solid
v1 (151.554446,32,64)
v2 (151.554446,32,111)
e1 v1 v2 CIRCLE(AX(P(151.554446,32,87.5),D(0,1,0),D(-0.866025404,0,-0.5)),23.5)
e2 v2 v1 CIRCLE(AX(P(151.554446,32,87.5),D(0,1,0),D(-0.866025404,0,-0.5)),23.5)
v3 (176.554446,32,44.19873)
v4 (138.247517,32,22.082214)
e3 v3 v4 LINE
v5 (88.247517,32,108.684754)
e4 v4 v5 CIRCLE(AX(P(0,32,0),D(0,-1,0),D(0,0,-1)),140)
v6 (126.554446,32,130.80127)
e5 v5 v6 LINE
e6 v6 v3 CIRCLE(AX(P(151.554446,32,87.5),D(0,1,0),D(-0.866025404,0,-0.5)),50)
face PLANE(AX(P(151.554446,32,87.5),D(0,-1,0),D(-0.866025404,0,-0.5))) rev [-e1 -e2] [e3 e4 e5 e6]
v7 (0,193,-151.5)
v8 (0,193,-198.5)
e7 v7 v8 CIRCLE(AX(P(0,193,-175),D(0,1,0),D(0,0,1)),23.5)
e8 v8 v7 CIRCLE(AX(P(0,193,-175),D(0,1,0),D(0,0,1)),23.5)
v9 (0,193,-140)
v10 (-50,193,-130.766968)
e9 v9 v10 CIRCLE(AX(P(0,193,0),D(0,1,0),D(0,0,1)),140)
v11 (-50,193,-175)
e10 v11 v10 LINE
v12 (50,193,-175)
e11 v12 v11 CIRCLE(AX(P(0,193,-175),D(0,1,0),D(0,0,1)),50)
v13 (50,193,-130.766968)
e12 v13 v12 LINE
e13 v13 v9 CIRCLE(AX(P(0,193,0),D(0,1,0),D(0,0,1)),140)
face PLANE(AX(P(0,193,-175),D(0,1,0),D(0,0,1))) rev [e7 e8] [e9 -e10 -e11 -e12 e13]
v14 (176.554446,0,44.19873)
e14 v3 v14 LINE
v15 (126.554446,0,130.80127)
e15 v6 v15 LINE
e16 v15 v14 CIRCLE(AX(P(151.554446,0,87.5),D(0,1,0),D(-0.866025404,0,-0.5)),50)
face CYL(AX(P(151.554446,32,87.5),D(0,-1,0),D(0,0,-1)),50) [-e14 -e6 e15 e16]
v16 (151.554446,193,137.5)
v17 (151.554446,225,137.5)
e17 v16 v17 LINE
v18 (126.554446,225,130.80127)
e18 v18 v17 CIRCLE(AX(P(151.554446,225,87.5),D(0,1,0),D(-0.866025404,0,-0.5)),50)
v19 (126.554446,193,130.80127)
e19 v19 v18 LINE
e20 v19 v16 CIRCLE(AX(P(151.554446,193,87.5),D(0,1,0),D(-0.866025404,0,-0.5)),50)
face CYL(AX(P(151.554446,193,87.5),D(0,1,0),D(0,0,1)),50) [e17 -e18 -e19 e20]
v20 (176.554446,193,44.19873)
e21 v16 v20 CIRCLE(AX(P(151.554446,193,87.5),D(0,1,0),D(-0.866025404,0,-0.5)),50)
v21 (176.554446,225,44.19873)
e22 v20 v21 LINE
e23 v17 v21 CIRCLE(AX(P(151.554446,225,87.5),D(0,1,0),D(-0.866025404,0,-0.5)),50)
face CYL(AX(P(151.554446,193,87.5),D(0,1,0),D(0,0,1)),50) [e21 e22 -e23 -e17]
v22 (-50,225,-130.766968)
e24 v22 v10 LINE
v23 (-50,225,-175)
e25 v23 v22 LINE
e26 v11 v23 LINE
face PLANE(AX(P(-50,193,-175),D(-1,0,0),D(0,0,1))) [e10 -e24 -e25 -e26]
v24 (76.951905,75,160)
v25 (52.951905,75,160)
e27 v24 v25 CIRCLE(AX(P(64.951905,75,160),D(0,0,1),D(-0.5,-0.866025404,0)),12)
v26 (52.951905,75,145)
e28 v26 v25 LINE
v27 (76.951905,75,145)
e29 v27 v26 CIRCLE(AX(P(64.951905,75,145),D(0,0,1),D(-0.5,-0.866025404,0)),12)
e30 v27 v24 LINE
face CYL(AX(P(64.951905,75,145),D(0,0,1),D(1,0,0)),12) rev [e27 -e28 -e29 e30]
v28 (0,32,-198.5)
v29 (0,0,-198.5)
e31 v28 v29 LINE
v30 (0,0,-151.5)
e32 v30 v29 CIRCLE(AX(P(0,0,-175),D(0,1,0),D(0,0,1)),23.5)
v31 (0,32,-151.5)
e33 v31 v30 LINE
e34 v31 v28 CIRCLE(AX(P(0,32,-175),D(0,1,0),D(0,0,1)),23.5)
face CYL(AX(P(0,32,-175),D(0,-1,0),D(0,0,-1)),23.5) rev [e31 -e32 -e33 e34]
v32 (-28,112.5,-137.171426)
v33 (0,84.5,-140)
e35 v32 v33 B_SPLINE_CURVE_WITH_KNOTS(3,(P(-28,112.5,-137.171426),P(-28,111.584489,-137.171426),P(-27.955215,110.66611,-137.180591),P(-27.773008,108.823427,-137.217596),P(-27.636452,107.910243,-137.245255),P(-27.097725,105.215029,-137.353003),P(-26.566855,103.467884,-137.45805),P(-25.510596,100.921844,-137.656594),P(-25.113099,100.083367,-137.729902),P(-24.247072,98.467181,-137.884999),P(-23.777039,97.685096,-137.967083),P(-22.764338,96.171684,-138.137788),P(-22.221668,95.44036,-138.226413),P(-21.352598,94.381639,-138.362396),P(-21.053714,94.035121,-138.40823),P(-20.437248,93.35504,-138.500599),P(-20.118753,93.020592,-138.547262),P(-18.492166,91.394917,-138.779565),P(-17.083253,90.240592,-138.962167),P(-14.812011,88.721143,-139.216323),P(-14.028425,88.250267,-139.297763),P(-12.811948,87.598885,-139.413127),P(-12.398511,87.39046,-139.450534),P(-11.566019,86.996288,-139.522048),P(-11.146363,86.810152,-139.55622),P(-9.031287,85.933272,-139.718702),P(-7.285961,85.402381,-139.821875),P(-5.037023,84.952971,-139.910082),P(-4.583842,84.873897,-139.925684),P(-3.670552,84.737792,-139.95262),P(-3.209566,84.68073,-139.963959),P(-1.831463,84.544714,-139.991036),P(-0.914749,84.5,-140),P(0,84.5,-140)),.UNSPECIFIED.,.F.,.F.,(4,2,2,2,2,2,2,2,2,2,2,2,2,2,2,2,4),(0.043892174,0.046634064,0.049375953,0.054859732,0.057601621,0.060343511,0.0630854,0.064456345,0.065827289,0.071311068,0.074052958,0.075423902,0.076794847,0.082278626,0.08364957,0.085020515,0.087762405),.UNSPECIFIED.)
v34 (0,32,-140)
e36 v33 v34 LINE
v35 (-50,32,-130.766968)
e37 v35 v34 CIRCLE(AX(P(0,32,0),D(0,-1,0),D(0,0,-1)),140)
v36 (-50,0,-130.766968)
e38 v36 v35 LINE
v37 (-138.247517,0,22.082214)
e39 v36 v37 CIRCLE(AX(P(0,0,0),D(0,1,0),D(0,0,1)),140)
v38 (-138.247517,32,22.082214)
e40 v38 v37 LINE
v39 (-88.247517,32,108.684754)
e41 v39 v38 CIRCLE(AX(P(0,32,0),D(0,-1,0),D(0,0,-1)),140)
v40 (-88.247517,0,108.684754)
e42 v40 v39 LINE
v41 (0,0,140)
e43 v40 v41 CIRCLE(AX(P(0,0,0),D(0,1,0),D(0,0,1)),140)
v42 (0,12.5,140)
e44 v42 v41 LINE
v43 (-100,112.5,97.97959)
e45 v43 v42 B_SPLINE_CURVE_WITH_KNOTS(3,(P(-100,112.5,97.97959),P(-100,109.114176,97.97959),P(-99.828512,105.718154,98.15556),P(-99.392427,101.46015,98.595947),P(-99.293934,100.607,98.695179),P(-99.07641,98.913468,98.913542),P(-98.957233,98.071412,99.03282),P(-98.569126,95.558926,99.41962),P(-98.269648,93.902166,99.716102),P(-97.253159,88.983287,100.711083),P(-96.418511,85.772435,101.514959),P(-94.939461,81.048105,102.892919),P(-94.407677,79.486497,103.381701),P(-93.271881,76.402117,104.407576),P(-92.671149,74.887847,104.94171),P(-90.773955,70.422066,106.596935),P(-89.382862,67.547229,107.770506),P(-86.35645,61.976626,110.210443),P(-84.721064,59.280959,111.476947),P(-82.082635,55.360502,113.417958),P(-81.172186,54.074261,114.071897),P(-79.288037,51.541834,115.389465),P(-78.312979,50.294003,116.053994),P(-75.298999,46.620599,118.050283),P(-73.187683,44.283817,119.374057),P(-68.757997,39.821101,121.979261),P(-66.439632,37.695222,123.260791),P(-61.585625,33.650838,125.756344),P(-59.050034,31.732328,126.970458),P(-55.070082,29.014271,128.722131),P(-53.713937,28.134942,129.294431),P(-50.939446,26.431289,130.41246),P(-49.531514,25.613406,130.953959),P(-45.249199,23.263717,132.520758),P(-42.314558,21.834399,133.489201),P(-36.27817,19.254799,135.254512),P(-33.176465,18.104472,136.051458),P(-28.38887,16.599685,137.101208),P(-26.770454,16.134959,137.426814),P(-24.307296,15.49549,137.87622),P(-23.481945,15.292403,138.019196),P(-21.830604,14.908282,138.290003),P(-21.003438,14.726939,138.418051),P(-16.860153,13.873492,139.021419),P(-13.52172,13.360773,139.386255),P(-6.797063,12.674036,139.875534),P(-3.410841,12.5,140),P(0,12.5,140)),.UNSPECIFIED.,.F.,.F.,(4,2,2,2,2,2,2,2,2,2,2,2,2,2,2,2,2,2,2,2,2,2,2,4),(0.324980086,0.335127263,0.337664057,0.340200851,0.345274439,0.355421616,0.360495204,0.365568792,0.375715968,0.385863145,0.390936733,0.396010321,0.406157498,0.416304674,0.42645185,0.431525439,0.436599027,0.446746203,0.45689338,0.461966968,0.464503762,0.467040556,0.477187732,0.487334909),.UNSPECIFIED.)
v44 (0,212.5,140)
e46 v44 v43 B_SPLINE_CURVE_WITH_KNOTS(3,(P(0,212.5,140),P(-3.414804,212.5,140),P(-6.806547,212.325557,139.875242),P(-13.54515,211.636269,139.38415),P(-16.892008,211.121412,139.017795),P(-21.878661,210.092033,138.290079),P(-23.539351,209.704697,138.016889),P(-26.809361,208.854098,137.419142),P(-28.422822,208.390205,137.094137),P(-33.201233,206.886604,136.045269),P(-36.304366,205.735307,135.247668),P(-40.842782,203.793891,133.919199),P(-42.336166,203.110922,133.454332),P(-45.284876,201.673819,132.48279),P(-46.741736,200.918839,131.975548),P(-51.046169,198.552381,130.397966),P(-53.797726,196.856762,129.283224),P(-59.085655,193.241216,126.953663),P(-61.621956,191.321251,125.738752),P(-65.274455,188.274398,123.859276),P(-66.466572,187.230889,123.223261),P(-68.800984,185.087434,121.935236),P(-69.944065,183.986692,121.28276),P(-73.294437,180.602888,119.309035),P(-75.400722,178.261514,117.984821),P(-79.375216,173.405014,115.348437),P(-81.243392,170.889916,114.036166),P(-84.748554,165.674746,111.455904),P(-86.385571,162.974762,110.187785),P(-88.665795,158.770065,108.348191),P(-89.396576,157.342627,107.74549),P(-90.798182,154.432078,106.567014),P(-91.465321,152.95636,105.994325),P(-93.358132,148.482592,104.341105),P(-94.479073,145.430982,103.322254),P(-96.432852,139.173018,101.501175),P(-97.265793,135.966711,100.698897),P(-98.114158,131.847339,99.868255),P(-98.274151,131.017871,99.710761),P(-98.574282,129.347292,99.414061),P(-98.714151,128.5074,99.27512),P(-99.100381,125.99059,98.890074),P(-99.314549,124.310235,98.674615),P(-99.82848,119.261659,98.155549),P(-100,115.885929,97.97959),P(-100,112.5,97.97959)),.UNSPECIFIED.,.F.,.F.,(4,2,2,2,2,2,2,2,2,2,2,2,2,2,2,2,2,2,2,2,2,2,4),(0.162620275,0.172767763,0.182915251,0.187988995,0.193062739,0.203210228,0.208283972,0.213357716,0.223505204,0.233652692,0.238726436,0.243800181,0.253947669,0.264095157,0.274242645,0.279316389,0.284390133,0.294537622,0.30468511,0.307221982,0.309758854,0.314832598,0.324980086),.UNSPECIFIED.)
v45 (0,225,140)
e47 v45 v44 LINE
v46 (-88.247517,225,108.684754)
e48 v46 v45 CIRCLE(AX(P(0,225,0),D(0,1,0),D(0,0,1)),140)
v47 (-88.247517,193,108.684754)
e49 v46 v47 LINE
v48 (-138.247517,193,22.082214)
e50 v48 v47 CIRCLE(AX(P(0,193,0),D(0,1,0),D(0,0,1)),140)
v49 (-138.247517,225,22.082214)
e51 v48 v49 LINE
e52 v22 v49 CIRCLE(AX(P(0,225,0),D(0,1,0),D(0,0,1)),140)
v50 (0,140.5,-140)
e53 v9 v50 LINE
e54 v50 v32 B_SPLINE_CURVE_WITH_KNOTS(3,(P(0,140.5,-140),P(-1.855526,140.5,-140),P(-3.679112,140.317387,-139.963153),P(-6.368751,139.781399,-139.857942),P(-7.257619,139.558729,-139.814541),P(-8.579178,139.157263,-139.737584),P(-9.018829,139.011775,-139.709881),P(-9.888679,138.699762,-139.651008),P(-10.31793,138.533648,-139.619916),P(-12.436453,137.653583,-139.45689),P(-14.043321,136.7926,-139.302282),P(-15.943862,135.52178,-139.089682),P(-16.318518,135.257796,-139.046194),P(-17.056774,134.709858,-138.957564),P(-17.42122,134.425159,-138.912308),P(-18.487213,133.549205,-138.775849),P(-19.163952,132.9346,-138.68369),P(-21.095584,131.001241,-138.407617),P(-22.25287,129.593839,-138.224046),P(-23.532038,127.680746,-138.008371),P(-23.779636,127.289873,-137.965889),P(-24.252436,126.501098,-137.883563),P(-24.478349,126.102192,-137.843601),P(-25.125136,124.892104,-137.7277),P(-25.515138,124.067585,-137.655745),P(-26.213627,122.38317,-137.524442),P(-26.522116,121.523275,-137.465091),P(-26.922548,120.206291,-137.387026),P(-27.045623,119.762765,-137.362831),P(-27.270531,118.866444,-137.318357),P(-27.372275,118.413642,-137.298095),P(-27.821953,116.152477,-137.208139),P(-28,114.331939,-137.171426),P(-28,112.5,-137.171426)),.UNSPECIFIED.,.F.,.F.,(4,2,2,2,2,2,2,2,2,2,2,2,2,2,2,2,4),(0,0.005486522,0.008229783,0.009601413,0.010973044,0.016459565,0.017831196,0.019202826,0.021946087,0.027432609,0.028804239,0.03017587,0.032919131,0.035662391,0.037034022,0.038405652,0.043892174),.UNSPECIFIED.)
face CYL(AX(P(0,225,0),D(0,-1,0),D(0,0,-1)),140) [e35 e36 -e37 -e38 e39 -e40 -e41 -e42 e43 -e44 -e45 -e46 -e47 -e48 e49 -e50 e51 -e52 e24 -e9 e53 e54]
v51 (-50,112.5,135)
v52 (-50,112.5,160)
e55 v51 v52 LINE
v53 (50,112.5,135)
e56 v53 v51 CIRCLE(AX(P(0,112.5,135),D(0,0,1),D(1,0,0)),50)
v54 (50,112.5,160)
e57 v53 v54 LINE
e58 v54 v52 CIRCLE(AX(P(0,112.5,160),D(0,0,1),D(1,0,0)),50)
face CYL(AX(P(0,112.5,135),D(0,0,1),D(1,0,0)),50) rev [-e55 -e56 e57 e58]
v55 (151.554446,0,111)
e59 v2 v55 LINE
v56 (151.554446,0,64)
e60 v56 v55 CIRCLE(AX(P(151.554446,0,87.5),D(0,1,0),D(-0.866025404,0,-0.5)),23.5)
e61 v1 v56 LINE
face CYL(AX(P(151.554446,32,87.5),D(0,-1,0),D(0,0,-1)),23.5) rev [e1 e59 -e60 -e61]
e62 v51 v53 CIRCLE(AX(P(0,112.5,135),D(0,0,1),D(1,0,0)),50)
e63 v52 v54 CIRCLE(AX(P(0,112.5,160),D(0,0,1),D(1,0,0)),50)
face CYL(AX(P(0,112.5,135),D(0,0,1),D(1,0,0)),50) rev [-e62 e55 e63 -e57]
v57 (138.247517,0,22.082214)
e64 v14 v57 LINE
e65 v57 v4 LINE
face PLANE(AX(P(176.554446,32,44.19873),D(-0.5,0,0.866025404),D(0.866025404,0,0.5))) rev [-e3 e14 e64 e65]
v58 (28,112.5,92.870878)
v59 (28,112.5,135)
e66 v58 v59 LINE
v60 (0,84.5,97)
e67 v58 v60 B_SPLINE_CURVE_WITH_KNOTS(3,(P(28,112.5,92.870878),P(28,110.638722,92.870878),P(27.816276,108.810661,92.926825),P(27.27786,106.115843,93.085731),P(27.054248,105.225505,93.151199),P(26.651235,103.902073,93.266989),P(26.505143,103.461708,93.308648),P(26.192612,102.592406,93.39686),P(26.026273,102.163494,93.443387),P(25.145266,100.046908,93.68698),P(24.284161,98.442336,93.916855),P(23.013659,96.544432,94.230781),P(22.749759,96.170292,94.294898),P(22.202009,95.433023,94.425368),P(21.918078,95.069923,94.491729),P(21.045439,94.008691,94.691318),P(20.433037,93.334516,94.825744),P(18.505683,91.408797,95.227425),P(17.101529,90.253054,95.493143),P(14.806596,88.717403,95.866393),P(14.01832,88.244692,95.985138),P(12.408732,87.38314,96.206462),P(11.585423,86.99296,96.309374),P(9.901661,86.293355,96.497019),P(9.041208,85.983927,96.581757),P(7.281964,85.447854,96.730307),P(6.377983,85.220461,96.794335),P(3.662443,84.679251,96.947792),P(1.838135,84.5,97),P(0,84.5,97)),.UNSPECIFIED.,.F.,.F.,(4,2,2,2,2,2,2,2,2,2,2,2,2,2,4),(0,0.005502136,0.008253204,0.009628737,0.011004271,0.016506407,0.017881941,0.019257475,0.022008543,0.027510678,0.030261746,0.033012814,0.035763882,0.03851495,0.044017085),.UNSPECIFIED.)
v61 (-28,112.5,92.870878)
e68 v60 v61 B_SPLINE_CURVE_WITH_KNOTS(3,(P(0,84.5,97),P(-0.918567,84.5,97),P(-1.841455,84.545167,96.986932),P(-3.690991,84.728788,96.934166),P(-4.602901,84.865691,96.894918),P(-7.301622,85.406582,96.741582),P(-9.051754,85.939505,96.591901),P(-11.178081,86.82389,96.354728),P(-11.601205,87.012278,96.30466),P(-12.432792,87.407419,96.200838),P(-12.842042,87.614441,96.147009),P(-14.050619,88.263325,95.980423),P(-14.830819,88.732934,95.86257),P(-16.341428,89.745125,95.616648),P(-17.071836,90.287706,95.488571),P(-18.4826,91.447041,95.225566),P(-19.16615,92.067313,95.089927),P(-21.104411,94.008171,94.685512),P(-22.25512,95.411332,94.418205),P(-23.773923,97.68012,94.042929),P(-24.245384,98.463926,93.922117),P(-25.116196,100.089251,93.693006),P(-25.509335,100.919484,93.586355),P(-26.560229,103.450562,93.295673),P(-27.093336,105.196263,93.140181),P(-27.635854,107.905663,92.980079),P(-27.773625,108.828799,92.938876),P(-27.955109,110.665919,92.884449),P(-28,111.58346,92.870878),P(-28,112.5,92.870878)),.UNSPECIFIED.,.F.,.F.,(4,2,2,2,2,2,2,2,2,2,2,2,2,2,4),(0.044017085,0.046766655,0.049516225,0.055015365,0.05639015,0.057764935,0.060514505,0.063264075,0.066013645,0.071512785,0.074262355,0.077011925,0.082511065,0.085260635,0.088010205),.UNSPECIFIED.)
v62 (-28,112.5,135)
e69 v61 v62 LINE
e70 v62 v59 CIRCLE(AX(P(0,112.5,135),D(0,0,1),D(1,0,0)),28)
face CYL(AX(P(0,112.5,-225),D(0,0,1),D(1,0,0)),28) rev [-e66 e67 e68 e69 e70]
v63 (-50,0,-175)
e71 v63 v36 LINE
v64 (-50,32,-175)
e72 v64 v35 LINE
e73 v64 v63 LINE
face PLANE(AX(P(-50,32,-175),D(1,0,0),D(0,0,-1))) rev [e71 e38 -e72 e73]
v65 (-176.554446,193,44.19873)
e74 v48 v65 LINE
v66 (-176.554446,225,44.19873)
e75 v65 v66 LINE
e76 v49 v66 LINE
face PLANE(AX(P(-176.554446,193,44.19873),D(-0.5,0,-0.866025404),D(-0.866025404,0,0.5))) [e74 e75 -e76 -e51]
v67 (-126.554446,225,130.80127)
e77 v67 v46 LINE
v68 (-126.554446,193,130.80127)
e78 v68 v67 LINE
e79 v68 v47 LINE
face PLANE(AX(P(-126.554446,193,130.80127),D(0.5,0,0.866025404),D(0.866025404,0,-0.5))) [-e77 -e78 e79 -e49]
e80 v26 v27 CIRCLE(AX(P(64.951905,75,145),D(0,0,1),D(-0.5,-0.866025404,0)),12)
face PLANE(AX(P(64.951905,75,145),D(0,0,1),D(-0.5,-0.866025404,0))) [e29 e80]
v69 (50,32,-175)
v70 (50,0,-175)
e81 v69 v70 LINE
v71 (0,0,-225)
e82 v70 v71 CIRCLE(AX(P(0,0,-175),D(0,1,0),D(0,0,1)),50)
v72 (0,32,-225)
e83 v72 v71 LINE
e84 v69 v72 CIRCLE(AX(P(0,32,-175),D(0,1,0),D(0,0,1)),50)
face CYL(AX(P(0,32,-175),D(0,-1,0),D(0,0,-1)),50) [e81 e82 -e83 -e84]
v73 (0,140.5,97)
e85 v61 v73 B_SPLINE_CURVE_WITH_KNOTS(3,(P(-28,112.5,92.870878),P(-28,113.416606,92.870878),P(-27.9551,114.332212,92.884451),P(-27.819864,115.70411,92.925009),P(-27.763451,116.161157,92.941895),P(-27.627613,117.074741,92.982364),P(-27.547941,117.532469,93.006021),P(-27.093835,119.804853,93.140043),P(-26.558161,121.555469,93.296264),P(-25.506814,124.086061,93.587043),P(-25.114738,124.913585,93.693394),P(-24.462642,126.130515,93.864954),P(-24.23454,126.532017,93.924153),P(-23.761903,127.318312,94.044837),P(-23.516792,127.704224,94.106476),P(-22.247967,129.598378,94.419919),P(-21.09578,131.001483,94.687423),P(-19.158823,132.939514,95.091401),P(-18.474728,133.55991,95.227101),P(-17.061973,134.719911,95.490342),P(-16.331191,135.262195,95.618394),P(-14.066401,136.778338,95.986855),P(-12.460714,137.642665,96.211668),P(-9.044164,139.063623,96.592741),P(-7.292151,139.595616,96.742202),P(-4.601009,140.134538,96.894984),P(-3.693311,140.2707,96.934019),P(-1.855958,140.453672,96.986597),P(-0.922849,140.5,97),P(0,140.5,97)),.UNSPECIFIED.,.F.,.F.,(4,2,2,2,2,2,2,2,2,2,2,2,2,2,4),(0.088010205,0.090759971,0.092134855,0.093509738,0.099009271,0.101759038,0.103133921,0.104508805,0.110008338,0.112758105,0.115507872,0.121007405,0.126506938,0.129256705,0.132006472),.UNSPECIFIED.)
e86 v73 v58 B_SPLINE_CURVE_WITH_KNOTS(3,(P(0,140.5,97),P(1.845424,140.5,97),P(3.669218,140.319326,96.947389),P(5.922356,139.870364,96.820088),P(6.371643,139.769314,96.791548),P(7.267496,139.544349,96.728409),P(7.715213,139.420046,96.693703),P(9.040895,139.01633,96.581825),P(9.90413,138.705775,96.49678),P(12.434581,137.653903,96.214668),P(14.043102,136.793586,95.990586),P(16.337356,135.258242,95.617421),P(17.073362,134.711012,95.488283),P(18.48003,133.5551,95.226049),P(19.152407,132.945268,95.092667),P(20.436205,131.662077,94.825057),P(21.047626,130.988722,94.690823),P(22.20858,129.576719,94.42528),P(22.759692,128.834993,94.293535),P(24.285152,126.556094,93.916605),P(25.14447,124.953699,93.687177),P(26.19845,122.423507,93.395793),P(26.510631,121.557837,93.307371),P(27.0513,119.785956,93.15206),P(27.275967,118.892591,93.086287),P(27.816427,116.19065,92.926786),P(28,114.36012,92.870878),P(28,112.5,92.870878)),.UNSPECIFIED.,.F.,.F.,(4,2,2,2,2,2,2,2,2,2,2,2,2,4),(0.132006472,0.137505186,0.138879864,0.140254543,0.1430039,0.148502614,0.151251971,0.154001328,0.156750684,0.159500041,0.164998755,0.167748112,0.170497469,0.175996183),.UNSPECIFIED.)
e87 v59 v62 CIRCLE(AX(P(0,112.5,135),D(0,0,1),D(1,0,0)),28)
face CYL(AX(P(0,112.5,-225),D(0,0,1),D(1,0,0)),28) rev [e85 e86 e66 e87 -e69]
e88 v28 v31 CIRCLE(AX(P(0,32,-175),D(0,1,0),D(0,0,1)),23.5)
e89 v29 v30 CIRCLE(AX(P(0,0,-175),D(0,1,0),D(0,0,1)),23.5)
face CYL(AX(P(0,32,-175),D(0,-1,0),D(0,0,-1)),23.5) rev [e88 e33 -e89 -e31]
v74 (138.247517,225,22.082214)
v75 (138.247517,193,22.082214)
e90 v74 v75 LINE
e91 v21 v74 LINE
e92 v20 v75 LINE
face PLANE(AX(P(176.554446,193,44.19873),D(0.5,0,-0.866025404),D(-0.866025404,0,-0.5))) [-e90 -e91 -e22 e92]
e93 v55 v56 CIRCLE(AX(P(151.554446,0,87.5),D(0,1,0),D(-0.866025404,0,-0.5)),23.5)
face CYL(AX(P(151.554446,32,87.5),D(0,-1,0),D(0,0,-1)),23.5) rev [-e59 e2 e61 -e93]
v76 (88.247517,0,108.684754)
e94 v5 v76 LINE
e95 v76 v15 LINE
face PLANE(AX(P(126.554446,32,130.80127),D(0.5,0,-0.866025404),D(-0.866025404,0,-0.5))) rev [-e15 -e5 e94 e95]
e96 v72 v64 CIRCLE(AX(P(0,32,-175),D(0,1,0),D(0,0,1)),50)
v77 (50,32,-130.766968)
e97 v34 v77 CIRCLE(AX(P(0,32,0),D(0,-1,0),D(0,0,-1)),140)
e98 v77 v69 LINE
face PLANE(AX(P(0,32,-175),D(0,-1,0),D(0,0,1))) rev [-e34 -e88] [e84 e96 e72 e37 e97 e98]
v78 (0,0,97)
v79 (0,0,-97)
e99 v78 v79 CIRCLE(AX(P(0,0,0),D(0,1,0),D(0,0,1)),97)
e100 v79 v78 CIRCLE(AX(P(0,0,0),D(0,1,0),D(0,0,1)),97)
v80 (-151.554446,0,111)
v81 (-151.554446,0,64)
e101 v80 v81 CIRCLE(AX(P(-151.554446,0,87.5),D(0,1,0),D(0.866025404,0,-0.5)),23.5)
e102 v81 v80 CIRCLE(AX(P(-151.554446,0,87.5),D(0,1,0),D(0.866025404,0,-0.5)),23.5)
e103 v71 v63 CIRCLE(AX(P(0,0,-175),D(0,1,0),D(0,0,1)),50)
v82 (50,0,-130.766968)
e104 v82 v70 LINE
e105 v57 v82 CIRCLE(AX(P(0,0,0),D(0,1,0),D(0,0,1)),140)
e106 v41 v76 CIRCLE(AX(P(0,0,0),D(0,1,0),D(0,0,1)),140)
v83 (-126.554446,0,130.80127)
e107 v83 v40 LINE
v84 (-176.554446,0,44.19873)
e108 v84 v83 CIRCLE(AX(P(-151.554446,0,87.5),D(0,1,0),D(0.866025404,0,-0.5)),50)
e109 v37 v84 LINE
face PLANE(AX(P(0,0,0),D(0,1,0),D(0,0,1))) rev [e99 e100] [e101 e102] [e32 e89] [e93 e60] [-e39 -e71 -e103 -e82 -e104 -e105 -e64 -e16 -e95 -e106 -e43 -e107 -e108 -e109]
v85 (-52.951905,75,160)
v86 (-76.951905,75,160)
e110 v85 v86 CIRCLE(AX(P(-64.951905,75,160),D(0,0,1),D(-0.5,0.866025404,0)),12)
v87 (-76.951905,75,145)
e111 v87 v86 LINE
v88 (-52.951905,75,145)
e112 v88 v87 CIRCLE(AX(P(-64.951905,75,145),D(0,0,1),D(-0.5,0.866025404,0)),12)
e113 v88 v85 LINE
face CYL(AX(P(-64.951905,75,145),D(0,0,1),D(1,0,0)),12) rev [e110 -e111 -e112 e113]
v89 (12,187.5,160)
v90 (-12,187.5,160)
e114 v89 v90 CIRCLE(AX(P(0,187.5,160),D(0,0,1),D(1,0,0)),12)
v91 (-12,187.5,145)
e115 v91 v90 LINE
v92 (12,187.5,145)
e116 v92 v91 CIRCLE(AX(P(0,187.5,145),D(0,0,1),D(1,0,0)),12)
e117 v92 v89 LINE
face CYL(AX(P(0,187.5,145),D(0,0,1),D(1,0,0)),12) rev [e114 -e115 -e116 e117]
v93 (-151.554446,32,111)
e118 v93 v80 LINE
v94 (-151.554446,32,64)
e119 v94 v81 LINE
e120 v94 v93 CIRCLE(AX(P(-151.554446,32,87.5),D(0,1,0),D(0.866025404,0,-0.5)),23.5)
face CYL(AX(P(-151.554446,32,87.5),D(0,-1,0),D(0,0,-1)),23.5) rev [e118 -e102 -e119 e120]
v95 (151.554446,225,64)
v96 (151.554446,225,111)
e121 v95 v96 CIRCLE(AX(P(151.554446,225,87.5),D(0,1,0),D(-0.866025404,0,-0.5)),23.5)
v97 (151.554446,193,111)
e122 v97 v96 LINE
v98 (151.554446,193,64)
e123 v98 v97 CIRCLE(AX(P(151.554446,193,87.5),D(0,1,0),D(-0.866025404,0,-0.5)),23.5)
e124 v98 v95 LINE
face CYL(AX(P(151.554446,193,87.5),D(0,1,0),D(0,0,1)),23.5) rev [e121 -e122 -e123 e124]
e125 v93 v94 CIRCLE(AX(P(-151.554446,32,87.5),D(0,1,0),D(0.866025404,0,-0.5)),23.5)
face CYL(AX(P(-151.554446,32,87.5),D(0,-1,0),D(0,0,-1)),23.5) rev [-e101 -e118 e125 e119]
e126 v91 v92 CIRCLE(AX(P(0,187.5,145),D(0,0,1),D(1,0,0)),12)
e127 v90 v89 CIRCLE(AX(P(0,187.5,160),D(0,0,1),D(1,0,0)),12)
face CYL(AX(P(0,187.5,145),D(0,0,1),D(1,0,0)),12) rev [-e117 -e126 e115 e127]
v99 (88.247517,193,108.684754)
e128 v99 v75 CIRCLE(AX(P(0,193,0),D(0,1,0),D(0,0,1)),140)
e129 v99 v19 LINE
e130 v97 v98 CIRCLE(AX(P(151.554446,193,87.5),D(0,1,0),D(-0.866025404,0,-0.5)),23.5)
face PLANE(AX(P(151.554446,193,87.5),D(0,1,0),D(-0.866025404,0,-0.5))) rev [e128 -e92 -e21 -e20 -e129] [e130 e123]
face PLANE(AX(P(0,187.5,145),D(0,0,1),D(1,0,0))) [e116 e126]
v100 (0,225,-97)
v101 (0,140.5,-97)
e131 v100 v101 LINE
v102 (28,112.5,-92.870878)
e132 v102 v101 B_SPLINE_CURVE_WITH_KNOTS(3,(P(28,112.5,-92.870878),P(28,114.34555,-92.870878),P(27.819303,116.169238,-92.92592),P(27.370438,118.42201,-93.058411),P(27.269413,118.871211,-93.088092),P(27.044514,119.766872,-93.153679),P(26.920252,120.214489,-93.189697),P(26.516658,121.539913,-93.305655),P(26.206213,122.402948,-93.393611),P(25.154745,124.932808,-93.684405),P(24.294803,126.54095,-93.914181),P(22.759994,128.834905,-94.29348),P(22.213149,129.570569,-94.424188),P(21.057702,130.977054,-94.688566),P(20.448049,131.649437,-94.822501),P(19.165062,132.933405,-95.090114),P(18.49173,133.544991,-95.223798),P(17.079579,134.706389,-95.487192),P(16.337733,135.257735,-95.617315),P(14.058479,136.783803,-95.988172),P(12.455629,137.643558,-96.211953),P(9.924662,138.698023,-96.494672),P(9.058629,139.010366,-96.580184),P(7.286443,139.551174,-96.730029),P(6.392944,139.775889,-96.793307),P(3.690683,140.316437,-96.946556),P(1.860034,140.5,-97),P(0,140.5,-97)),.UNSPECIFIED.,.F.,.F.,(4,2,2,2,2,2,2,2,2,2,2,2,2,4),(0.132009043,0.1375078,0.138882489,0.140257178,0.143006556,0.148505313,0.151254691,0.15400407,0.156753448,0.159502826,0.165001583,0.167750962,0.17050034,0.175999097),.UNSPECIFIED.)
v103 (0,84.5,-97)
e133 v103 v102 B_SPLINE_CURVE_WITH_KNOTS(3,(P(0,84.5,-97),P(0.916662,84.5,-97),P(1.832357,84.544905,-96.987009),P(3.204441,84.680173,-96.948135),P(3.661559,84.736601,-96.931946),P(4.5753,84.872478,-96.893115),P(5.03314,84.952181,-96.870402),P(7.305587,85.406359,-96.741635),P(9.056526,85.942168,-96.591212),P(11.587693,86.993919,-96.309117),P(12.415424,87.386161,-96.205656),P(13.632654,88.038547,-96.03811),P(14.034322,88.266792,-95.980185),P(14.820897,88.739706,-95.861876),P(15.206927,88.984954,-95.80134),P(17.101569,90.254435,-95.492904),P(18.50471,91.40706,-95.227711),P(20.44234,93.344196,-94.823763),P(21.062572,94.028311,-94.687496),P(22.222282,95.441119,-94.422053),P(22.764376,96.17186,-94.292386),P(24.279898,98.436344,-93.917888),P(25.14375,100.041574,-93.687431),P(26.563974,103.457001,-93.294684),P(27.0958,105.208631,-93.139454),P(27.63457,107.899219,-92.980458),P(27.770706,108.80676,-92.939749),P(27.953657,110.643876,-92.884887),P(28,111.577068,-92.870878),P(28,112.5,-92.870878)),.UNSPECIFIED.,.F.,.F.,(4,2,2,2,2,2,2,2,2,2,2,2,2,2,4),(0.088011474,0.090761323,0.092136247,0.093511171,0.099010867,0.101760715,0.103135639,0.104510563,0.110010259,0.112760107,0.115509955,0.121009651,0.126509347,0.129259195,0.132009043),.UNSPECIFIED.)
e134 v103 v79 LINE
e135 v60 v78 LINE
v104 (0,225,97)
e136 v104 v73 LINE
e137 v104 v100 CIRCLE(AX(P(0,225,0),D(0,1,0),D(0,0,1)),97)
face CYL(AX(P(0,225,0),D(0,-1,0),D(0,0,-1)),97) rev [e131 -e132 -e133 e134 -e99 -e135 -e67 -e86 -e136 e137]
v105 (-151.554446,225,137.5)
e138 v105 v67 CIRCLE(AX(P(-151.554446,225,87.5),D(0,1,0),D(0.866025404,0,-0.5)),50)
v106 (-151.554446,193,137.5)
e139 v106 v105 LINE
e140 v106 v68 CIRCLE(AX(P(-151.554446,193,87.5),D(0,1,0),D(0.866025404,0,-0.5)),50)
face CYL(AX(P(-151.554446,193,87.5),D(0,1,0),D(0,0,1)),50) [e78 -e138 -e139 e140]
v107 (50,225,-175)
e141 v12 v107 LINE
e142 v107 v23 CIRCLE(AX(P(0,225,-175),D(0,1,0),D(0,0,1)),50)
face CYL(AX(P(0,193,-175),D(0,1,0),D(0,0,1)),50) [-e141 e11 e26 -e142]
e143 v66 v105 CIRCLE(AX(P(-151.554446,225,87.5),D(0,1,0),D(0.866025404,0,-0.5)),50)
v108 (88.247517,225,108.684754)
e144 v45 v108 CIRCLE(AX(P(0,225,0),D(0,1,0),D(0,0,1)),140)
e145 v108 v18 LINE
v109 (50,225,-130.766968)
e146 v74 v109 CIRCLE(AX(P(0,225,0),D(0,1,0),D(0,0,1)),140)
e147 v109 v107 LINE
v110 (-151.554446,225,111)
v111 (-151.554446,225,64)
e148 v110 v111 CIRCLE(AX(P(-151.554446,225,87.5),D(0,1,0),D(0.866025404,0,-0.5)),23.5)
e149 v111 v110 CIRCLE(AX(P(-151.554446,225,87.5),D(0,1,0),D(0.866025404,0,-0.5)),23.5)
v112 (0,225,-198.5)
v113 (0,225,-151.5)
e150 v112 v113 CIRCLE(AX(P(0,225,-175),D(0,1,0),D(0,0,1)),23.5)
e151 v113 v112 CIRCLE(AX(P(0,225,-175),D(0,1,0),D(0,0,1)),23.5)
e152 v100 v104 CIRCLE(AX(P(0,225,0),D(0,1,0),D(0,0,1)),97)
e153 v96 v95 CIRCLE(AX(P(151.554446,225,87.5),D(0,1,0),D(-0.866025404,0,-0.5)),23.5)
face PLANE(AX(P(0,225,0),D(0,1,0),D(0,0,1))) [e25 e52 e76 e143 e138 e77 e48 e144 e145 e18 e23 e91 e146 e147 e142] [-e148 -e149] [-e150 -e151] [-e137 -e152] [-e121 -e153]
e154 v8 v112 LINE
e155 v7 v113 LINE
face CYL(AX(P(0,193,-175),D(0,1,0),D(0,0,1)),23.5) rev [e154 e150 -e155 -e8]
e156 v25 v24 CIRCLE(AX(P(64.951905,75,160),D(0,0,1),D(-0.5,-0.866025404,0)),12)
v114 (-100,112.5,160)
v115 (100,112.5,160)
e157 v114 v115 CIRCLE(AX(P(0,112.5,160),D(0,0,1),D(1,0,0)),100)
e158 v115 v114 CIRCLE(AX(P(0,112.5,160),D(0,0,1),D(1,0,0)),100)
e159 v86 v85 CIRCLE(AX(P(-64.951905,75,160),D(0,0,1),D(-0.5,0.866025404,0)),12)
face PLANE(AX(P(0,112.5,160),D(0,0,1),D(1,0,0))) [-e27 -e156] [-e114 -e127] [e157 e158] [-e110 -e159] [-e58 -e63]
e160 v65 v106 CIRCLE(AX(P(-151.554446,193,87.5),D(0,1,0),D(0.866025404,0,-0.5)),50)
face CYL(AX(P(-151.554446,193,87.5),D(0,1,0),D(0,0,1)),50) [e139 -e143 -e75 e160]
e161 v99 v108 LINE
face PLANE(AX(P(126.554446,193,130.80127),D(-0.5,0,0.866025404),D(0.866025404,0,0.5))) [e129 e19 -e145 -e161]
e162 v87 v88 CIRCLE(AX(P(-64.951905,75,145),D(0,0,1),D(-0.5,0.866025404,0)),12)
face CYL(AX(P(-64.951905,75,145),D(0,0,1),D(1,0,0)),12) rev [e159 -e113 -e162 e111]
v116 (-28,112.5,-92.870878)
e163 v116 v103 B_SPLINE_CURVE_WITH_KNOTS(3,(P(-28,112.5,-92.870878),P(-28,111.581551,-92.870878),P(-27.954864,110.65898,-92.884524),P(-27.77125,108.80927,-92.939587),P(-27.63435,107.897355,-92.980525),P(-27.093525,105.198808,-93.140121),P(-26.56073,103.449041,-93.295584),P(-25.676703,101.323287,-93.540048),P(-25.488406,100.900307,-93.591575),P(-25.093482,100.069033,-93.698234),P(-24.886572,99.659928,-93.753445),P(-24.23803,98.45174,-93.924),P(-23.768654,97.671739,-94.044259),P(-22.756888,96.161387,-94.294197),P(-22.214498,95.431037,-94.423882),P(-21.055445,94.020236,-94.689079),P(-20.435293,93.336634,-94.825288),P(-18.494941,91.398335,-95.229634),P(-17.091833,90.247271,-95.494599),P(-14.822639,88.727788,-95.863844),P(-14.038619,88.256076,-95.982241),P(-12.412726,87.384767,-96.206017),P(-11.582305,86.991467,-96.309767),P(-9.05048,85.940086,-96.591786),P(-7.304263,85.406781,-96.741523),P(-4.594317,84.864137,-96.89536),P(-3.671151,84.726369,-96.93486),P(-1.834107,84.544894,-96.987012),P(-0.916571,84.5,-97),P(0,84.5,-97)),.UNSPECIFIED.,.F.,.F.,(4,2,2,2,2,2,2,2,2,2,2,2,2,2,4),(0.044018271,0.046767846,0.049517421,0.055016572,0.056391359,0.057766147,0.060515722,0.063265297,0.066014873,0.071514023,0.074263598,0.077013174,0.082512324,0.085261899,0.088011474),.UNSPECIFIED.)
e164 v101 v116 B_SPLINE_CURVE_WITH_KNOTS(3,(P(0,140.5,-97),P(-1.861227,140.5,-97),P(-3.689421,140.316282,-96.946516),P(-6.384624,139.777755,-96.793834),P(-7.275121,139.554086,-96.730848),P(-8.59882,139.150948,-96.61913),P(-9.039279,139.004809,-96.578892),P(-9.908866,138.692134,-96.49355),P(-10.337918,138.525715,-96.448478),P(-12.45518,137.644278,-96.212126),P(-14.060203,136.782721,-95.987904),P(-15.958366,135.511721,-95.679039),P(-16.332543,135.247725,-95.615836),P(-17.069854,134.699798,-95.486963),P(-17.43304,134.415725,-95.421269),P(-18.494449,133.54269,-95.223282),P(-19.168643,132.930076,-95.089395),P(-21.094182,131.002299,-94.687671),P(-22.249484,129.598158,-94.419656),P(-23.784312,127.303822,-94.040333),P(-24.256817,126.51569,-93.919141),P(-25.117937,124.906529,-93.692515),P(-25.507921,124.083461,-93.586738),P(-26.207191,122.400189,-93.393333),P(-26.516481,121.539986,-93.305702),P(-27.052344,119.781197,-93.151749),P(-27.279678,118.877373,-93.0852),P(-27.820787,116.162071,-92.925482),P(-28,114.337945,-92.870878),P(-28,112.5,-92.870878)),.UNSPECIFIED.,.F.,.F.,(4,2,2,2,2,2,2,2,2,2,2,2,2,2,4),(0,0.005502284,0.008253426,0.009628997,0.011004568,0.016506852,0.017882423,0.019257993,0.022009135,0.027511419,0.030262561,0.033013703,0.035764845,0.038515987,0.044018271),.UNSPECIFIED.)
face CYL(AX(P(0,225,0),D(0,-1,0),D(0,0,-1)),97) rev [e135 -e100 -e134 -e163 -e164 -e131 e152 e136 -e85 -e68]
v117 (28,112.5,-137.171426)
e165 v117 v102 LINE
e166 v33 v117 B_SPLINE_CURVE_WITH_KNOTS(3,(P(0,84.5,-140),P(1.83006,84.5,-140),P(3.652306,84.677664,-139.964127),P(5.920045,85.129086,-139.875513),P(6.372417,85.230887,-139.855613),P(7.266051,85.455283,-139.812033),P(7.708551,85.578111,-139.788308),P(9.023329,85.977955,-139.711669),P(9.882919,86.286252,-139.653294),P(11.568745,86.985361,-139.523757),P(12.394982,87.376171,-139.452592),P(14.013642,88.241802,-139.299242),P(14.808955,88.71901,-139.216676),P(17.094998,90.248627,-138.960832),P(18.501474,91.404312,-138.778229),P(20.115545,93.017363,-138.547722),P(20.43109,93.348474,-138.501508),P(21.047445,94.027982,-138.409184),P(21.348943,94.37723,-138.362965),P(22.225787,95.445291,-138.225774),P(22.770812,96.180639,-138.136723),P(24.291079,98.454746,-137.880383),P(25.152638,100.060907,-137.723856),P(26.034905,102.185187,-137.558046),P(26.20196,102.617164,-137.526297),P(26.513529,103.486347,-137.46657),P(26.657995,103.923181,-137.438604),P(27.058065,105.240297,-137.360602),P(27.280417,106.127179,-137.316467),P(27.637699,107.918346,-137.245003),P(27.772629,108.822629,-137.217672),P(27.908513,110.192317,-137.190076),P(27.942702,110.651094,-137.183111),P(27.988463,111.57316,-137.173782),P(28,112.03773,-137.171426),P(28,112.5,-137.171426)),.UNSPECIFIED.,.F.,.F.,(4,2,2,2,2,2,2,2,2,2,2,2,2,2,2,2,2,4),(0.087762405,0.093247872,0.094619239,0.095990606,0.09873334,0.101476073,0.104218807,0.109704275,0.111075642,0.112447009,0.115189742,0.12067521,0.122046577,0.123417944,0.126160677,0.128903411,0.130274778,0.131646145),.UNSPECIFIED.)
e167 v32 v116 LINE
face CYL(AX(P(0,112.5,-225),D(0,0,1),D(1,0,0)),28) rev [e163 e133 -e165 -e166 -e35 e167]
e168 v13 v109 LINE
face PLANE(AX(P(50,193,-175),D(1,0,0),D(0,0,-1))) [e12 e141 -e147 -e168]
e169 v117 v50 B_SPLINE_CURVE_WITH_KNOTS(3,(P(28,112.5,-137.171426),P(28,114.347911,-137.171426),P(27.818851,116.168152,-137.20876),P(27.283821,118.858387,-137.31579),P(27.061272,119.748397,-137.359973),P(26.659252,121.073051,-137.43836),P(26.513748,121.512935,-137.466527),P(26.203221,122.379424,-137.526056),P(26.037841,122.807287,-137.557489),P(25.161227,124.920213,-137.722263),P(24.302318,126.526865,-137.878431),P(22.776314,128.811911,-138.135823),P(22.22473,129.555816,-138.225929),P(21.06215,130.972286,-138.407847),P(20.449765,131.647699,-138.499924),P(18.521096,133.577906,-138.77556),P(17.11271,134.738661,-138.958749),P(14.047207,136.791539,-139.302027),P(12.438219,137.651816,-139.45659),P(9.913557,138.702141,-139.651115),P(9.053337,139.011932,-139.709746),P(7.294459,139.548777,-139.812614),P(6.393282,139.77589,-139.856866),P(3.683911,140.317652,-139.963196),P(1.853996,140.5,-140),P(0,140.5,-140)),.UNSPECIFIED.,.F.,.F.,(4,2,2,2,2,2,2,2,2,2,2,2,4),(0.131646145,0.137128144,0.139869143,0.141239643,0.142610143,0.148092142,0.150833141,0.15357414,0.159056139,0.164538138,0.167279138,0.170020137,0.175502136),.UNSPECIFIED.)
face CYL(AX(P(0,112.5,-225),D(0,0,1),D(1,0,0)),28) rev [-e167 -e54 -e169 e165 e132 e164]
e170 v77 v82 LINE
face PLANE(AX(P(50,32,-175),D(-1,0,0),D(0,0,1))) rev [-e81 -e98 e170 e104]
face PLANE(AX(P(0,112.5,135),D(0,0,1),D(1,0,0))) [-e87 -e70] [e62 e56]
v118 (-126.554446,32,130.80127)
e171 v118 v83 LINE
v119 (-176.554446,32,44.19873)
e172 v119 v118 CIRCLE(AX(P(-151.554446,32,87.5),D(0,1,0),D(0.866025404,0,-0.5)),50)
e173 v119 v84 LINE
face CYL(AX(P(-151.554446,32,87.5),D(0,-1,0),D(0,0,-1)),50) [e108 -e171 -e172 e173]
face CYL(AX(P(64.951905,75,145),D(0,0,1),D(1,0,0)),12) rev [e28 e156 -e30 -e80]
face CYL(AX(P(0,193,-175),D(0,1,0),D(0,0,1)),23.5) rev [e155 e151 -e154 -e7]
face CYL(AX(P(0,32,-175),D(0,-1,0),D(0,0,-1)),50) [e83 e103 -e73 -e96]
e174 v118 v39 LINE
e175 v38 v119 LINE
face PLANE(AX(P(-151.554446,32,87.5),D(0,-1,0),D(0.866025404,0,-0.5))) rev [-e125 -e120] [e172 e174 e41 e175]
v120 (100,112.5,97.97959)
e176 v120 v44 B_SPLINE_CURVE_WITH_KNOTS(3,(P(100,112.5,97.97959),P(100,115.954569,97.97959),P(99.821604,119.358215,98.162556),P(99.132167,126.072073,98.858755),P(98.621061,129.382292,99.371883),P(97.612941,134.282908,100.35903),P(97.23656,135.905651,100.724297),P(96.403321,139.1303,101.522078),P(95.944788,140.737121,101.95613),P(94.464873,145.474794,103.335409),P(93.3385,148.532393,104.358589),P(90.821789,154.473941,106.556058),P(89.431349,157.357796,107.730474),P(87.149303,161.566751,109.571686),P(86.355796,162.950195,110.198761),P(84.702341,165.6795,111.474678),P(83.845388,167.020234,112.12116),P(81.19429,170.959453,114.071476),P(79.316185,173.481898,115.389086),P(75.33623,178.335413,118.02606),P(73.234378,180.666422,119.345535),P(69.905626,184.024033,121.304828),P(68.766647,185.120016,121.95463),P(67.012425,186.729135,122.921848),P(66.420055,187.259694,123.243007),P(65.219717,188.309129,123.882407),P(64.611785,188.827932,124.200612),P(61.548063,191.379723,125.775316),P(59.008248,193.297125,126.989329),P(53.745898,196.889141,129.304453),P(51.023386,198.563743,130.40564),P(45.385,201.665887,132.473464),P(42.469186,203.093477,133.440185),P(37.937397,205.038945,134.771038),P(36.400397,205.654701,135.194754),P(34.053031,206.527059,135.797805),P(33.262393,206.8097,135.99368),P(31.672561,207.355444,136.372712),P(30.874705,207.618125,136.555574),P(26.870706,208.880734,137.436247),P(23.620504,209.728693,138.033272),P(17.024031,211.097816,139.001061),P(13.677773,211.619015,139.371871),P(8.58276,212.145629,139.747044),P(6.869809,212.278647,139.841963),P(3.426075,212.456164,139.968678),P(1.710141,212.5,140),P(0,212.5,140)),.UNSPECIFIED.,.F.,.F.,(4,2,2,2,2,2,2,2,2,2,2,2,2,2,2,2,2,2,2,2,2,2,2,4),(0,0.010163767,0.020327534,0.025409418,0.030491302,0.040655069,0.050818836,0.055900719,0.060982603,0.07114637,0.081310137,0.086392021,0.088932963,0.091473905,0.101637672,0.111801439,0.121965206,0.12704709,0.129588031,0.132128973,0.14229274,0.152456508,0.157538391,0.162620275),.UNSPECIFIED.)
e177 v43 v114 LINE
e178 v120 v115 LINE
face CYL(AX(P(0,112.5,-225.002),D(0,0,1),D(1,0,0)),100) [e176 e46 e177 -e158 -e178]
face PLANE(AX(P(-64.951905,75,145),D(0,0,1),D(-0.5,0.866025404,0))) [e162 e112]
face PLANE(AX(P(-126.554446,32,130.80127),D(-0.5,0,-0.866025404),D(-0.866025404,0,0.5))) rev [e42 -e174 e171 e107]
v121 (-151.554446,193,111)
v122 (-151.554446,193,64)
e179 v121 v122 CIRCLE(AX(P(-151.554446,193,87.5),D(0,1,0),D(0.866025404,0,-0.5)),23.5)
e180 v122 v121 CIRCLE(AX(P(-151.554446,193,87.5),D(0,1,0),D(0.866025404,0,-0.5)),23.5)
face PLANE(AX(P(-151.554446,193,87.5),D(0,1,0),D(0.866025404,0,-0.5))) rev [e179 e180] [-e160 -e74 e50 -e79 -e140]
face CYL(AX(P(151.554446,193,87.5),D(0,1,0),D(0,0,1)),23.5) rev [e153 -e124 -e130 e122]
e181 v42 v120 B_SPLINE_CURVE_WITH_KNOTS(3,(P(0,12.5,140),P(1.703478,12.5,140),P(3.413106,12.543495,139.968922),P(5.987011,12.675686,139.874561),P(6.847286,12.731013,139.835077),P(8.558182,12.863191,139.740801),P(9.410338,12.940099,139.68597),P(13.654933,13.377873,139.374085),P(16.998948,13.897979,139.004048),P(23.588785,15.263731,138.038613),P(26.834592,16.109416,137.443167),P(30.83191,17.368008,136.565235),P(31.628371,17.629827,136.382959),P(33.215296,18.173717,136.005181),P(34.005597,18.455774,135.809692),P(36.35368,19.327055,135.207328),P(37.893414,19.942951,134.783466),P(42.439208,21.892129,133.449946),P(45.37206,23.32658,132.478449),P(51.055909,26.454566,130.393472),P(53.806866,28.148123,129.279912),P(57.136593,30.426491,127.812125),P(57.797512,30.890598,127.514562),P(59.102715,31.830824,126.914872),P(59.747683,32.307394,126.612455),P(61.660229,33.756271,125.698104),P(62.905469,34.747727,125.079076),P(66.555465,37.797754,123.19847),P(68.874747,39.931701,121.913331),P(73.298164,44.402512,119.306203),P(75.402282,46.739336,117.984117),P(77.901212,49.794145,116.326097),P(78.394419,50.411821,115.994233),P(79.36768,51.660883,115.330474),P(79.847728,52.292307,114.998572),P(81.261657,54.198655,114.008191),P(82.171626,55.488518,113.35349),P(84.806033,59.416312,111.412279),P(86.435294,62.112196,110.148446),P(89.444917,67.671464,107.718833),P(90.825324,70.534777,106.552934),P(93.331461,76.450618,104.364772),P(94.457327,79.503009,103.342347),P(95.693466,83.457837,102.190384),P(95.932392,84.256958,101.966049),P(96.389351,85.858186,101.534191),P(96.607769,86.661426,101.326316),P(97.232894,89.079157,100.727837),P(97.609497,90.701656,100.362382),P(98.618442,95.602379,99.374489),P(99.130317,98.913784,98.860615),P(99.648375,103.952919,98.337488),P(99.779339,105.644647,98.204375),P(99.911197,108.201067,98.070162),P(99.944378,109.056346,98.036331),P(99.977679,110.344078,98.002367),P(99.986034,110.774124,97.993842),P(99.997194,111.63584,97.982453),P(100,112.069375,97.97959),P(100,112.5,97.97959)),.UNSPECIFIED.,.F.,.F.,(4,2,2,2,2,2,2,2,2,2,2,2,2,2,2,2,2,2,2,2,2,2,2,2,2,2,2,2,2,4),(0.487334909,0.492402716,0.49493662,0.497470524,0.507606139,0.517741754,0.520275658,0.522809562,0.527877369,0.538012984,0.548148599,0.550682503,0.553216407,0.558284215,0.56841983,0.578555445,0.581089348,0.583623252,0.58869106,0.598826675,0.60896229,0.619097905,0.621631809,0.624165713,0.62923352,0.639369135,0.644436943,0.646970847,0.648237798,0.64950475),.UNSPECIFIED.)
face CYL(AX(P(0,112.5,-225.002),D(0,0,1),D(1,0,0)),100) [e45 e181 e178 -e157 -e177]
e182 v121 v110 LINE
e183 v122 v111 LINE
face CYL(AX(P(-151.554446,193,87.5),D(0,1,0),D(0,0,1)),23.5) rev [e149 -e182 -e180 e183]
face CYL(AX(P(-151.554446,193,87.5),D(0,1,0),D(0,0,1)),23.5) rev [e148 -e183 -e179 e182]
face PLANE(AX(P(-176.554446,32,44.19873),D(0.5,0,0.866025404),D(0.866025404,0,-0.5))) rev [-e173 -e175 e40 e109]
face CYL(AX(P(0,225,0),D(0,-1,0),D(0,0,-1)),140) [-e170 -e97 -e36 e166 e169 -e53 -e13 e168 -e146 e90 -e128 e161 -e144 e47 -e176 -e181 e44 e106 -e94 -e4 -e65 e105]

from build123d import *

# Parameters (mm, degrees)
BODY_TUBE_SKETCH_R                = 140
BODY_TUBE_SKETCH_R_2              = 97
BODY_TUBE_DEPTH                   = 225
FLANGE_LUG_SKETCH_R               = 23.5
FLANGE_LUG_DEPTH                  = 32
FLANGE_LUG_PATTERN_3X_COUNT       = 3
FLANGE_LUG_MIRROR_COPY_1_SKETCH_R = 23.5
FLANGE_LUG_MIRROR_COPY_1_DEPTH    = 32
FLANGE_LUG_MIRROR_COPY_2_SKETCH_R = 23.5
FLANGE_LUG_MIRROR_COPY_2_DEPTH    = 32
FLANGE_LUG_MIRROR_COPY_3_SKETCH_R = 23.5
FLANGE_LUG_MIRROR_COPY_3_DEPTH    = 32
SIDE_BOSS_REACH                   = 491.361
SIDE_BOSS_END_RADIUS              = 140
SIDE_BOSS_SKETCH_R                = 100
SIDE_COUNTERBORE_SKETCH_R         = 50
SIDE_COUNTERBORE_DEPTH            = 25
SIDE_BORE_SKETCH_R                = 28
SIDE_THROUGH_BORE_DEPTH           = 470.945948606
SIDE_BOLT_HOLE_SKETCH_R           = 12
SIDE_BOLT_HOLE_DEPTH              = 15
SIDE_BOLT_HOLE_PATTERN_3X_COUNT   = 3


with BuildPart() as part:
    # Body Tube Sketch → Body Tube (new body)
    with BuildSketch(Plane(origin=(0, 0, 0), x_dir=(1, 0, 0), z_dir=(0, 1, 0))):
        with Locations(Location((0, 0, 0), (0, 0, 270))):
            Circle(BODY_TUBE_SKETCH_R)
        with Locations(Location((0, 0, 0), (0, 0, 270))):
            Circle(BODY_TUBE_SKETCH_R_2, mode=Mode.SUBTRACT)
    body_tube = extrude(amount=BODY_TUBE_DEPTH)

    # Flange Lug Sketch → Flange Lug (add)
    with BuildSketch(Plane(origin=(0, 225, 0), x_dir=(1, 0, 0), z_dir=(0, 1, 0))):
        with BuildLine():
            Line((-50, 175), (-50, 110.834659577))
            Line((-50, 110.834659577), (50, 110.834659577))
            Line((50, 110.834659577), (50, 175))
            ThreePointArc((50, 175), (0, 225), (-50, 175))
        make_face()
        with Locations(Location((0, 175, 0), (0, 0, 270))):
            Circle(FLANGE_LUG_SKETCH_R, mode=Mode.SUBTRACT)
    flange_lug = extrude(amount=-FLANGE_LUG_DEPTH)

    # Flange Lug Pattern 3x: Flange Lug ×3 about axis
    flange_lug_pattern_3x_axis = Axis((0, 0, 0), (0, 1, 0))
    for i in range(1, FLANGE_LUG_PATTERN_3X_COUNT):
        add(flange_lug.rotate(flange_lug_pattern_3x_axis, i * 360 / FLANGE_LUG_PATTERN_3X_COUNT))

    # Flange Lug Mirror: Body Tube across plane
    add(body_tube.mirror(Plane.ZX.offset(112.5)))

    # Flange Lug Mirror copy 1 sketch → Flange Lug Mirror copy 1 (add)
    with BuildSketch(Plane(origin=(0, 0, 0), x_dir=(-0.4999999999999998, 0, -0.8660254037844387), z_dir=(0, -1, 0))):
        with BuildLine():
            Line((-50, -175), (-50, -110.834659577))
            Line((-50, -110.834659577), (50, -110.834659577))
            Line((50, -110.834659577), (50, -175))
            ThreePointArc((50, -175), (0, -225), (-50, -175))
        make_face()
        with Locations((0, -175)):
            Circle(FLANGE_LUG_MIRROR_COPY_1_SKETCH_R, mode=Mode.SUBTRACT)
    extrude(amount=-FLANGE_LUG_MIRROR_COPY_1_DEPTH)

    # Flange Lug Mirror copy 2 sketch → Flange Lug Mirror copy 2 (add)
    with BuildSketch(Plane(origin=(0, 0, 0), x_dir=(-0.5000000000000004, 0, 0.8660254037844384), z_dir=(0, -1, 0))):
        with BuildLine():
            Line((-50, -175), (-50, -110.834659577))
            Line((-50, -110.834659577), (50, -110.834659577))
            Line((50, -110.834659577), (50, -175))
            ThreePointArc((50, -175), (0, -225), (-50, -175))
        make_face()
        with Locations((0, -175)):
            Circle(FLANGE_LUG_MIRROR_COPY_2_SKETCH_R, mode=Mode.SUBTRACT)
    extrude(amount=-FLANGE_LUG_MIRROR_COPY_2_DEPTH)

    # Flange Lug Mirror copy 3 sketch → Flange Lug Mirror copy 3 (add)
    with BuildSketch(Plane.XZ):
        with BuildLine():
            Line((-50, -175), (-50, -110.834659577))
            Line((-50, -110.834659577), (50, -110.834659577))
            Line((50, -110.834659577), (50, -175))
            ThreePointArc((50, -175), (0, -225), (-50, -175))
        make_face()
        with Locations((0, -175)):
            Circle(FLANGE_LUG_MIRROR_COPY_3_SKETCH_R, mode=Mode.SUBTRACT)
    extrude(amount=-FLANGE_LUG_MIRROR_COPY_3_DEPTH)

    # Side Boss: up to this cylinder (the profile starts outside it)
    side_boss_end = Plane(origin=(0, 112.5, 0), z_dir=(0, -1, 0)) * Cylinder(SIDE_BOSS_END_RADIUS, 1263.722, mode=Mode.PRIVATE)
    # Side Boss Sketch → Side Boss (add, up to the surface)
    with BuildSketch(Plane.XY.offset(160), mode=Mode.PRIVATE) as side_boss_sk1:
        with Locations((0, 112.5)):
            Circle(SIDE_BOSS_SKETCH_R)
    side_boss_tool1 = extrude(side_boss_sk1.sketch, amount=-SIDE_BOSS_REACH, mode=Mode.PRIVATE) - side_boss_end
    add(side_boss_tool1.solids().sort_by_distance((0, 112.5, 160))[0])

    # Side Counterbore Sketch → Side Counterbore (cut)
    with BuildSketch(Plane.XY.offset(160)):
        with Locations((0, 112.5)):
            Circle(SIDE_COUNTERBORE_SKETCH_R)
    extrude(amount=-SIDE_COUNTERBORE_DEPTH, mode=Mode.SUBTRACT)

    # Side Bore Sketch → Side Through Bore (cut, through all)
    with BuildSketch(Plane.XY.offset(135)):
        with Locations((0, 112.5)):
            Circle(SIDE_BORE_SKETCH_R)
    extrude(amount=-SIDE_THROUGH_BORE_DEPTH, mode=Mode.SUBTRACT)

    # Side Bolt Hole Sketch → Side Bolt Hole (cut)
    with BuildSketch(Plane.XY.offset(160)):
        with Locations((0, 187.5)):
            Circle(SIDE_BOLT_HOLE_SKETCH_R)
    side_bolt_hole = extrude(amount=-SIDE_BOLT_HOLE_DEPTH, mode=Mode.SUBTRACT)

    # Side Bolt Hole Pattern 3x: Side Bolt Hole ×3 about axis
    side_bolt_hole_pattern_3x_axis = Axis((0, 112.5, 0), (0, 0, 1))
    for i in range(1, SIDE_BOLT_HOLE_PATTERN_3X_COUNT):
        add(side_bolt_hole.rotate(side_bolt_hole_pattern_3x_axis, i * 360 / SIDE_BOLT_HOLE_PATTERN_3X_COUNT), mode=Mode.SUBTRACT)


solid = part.part
